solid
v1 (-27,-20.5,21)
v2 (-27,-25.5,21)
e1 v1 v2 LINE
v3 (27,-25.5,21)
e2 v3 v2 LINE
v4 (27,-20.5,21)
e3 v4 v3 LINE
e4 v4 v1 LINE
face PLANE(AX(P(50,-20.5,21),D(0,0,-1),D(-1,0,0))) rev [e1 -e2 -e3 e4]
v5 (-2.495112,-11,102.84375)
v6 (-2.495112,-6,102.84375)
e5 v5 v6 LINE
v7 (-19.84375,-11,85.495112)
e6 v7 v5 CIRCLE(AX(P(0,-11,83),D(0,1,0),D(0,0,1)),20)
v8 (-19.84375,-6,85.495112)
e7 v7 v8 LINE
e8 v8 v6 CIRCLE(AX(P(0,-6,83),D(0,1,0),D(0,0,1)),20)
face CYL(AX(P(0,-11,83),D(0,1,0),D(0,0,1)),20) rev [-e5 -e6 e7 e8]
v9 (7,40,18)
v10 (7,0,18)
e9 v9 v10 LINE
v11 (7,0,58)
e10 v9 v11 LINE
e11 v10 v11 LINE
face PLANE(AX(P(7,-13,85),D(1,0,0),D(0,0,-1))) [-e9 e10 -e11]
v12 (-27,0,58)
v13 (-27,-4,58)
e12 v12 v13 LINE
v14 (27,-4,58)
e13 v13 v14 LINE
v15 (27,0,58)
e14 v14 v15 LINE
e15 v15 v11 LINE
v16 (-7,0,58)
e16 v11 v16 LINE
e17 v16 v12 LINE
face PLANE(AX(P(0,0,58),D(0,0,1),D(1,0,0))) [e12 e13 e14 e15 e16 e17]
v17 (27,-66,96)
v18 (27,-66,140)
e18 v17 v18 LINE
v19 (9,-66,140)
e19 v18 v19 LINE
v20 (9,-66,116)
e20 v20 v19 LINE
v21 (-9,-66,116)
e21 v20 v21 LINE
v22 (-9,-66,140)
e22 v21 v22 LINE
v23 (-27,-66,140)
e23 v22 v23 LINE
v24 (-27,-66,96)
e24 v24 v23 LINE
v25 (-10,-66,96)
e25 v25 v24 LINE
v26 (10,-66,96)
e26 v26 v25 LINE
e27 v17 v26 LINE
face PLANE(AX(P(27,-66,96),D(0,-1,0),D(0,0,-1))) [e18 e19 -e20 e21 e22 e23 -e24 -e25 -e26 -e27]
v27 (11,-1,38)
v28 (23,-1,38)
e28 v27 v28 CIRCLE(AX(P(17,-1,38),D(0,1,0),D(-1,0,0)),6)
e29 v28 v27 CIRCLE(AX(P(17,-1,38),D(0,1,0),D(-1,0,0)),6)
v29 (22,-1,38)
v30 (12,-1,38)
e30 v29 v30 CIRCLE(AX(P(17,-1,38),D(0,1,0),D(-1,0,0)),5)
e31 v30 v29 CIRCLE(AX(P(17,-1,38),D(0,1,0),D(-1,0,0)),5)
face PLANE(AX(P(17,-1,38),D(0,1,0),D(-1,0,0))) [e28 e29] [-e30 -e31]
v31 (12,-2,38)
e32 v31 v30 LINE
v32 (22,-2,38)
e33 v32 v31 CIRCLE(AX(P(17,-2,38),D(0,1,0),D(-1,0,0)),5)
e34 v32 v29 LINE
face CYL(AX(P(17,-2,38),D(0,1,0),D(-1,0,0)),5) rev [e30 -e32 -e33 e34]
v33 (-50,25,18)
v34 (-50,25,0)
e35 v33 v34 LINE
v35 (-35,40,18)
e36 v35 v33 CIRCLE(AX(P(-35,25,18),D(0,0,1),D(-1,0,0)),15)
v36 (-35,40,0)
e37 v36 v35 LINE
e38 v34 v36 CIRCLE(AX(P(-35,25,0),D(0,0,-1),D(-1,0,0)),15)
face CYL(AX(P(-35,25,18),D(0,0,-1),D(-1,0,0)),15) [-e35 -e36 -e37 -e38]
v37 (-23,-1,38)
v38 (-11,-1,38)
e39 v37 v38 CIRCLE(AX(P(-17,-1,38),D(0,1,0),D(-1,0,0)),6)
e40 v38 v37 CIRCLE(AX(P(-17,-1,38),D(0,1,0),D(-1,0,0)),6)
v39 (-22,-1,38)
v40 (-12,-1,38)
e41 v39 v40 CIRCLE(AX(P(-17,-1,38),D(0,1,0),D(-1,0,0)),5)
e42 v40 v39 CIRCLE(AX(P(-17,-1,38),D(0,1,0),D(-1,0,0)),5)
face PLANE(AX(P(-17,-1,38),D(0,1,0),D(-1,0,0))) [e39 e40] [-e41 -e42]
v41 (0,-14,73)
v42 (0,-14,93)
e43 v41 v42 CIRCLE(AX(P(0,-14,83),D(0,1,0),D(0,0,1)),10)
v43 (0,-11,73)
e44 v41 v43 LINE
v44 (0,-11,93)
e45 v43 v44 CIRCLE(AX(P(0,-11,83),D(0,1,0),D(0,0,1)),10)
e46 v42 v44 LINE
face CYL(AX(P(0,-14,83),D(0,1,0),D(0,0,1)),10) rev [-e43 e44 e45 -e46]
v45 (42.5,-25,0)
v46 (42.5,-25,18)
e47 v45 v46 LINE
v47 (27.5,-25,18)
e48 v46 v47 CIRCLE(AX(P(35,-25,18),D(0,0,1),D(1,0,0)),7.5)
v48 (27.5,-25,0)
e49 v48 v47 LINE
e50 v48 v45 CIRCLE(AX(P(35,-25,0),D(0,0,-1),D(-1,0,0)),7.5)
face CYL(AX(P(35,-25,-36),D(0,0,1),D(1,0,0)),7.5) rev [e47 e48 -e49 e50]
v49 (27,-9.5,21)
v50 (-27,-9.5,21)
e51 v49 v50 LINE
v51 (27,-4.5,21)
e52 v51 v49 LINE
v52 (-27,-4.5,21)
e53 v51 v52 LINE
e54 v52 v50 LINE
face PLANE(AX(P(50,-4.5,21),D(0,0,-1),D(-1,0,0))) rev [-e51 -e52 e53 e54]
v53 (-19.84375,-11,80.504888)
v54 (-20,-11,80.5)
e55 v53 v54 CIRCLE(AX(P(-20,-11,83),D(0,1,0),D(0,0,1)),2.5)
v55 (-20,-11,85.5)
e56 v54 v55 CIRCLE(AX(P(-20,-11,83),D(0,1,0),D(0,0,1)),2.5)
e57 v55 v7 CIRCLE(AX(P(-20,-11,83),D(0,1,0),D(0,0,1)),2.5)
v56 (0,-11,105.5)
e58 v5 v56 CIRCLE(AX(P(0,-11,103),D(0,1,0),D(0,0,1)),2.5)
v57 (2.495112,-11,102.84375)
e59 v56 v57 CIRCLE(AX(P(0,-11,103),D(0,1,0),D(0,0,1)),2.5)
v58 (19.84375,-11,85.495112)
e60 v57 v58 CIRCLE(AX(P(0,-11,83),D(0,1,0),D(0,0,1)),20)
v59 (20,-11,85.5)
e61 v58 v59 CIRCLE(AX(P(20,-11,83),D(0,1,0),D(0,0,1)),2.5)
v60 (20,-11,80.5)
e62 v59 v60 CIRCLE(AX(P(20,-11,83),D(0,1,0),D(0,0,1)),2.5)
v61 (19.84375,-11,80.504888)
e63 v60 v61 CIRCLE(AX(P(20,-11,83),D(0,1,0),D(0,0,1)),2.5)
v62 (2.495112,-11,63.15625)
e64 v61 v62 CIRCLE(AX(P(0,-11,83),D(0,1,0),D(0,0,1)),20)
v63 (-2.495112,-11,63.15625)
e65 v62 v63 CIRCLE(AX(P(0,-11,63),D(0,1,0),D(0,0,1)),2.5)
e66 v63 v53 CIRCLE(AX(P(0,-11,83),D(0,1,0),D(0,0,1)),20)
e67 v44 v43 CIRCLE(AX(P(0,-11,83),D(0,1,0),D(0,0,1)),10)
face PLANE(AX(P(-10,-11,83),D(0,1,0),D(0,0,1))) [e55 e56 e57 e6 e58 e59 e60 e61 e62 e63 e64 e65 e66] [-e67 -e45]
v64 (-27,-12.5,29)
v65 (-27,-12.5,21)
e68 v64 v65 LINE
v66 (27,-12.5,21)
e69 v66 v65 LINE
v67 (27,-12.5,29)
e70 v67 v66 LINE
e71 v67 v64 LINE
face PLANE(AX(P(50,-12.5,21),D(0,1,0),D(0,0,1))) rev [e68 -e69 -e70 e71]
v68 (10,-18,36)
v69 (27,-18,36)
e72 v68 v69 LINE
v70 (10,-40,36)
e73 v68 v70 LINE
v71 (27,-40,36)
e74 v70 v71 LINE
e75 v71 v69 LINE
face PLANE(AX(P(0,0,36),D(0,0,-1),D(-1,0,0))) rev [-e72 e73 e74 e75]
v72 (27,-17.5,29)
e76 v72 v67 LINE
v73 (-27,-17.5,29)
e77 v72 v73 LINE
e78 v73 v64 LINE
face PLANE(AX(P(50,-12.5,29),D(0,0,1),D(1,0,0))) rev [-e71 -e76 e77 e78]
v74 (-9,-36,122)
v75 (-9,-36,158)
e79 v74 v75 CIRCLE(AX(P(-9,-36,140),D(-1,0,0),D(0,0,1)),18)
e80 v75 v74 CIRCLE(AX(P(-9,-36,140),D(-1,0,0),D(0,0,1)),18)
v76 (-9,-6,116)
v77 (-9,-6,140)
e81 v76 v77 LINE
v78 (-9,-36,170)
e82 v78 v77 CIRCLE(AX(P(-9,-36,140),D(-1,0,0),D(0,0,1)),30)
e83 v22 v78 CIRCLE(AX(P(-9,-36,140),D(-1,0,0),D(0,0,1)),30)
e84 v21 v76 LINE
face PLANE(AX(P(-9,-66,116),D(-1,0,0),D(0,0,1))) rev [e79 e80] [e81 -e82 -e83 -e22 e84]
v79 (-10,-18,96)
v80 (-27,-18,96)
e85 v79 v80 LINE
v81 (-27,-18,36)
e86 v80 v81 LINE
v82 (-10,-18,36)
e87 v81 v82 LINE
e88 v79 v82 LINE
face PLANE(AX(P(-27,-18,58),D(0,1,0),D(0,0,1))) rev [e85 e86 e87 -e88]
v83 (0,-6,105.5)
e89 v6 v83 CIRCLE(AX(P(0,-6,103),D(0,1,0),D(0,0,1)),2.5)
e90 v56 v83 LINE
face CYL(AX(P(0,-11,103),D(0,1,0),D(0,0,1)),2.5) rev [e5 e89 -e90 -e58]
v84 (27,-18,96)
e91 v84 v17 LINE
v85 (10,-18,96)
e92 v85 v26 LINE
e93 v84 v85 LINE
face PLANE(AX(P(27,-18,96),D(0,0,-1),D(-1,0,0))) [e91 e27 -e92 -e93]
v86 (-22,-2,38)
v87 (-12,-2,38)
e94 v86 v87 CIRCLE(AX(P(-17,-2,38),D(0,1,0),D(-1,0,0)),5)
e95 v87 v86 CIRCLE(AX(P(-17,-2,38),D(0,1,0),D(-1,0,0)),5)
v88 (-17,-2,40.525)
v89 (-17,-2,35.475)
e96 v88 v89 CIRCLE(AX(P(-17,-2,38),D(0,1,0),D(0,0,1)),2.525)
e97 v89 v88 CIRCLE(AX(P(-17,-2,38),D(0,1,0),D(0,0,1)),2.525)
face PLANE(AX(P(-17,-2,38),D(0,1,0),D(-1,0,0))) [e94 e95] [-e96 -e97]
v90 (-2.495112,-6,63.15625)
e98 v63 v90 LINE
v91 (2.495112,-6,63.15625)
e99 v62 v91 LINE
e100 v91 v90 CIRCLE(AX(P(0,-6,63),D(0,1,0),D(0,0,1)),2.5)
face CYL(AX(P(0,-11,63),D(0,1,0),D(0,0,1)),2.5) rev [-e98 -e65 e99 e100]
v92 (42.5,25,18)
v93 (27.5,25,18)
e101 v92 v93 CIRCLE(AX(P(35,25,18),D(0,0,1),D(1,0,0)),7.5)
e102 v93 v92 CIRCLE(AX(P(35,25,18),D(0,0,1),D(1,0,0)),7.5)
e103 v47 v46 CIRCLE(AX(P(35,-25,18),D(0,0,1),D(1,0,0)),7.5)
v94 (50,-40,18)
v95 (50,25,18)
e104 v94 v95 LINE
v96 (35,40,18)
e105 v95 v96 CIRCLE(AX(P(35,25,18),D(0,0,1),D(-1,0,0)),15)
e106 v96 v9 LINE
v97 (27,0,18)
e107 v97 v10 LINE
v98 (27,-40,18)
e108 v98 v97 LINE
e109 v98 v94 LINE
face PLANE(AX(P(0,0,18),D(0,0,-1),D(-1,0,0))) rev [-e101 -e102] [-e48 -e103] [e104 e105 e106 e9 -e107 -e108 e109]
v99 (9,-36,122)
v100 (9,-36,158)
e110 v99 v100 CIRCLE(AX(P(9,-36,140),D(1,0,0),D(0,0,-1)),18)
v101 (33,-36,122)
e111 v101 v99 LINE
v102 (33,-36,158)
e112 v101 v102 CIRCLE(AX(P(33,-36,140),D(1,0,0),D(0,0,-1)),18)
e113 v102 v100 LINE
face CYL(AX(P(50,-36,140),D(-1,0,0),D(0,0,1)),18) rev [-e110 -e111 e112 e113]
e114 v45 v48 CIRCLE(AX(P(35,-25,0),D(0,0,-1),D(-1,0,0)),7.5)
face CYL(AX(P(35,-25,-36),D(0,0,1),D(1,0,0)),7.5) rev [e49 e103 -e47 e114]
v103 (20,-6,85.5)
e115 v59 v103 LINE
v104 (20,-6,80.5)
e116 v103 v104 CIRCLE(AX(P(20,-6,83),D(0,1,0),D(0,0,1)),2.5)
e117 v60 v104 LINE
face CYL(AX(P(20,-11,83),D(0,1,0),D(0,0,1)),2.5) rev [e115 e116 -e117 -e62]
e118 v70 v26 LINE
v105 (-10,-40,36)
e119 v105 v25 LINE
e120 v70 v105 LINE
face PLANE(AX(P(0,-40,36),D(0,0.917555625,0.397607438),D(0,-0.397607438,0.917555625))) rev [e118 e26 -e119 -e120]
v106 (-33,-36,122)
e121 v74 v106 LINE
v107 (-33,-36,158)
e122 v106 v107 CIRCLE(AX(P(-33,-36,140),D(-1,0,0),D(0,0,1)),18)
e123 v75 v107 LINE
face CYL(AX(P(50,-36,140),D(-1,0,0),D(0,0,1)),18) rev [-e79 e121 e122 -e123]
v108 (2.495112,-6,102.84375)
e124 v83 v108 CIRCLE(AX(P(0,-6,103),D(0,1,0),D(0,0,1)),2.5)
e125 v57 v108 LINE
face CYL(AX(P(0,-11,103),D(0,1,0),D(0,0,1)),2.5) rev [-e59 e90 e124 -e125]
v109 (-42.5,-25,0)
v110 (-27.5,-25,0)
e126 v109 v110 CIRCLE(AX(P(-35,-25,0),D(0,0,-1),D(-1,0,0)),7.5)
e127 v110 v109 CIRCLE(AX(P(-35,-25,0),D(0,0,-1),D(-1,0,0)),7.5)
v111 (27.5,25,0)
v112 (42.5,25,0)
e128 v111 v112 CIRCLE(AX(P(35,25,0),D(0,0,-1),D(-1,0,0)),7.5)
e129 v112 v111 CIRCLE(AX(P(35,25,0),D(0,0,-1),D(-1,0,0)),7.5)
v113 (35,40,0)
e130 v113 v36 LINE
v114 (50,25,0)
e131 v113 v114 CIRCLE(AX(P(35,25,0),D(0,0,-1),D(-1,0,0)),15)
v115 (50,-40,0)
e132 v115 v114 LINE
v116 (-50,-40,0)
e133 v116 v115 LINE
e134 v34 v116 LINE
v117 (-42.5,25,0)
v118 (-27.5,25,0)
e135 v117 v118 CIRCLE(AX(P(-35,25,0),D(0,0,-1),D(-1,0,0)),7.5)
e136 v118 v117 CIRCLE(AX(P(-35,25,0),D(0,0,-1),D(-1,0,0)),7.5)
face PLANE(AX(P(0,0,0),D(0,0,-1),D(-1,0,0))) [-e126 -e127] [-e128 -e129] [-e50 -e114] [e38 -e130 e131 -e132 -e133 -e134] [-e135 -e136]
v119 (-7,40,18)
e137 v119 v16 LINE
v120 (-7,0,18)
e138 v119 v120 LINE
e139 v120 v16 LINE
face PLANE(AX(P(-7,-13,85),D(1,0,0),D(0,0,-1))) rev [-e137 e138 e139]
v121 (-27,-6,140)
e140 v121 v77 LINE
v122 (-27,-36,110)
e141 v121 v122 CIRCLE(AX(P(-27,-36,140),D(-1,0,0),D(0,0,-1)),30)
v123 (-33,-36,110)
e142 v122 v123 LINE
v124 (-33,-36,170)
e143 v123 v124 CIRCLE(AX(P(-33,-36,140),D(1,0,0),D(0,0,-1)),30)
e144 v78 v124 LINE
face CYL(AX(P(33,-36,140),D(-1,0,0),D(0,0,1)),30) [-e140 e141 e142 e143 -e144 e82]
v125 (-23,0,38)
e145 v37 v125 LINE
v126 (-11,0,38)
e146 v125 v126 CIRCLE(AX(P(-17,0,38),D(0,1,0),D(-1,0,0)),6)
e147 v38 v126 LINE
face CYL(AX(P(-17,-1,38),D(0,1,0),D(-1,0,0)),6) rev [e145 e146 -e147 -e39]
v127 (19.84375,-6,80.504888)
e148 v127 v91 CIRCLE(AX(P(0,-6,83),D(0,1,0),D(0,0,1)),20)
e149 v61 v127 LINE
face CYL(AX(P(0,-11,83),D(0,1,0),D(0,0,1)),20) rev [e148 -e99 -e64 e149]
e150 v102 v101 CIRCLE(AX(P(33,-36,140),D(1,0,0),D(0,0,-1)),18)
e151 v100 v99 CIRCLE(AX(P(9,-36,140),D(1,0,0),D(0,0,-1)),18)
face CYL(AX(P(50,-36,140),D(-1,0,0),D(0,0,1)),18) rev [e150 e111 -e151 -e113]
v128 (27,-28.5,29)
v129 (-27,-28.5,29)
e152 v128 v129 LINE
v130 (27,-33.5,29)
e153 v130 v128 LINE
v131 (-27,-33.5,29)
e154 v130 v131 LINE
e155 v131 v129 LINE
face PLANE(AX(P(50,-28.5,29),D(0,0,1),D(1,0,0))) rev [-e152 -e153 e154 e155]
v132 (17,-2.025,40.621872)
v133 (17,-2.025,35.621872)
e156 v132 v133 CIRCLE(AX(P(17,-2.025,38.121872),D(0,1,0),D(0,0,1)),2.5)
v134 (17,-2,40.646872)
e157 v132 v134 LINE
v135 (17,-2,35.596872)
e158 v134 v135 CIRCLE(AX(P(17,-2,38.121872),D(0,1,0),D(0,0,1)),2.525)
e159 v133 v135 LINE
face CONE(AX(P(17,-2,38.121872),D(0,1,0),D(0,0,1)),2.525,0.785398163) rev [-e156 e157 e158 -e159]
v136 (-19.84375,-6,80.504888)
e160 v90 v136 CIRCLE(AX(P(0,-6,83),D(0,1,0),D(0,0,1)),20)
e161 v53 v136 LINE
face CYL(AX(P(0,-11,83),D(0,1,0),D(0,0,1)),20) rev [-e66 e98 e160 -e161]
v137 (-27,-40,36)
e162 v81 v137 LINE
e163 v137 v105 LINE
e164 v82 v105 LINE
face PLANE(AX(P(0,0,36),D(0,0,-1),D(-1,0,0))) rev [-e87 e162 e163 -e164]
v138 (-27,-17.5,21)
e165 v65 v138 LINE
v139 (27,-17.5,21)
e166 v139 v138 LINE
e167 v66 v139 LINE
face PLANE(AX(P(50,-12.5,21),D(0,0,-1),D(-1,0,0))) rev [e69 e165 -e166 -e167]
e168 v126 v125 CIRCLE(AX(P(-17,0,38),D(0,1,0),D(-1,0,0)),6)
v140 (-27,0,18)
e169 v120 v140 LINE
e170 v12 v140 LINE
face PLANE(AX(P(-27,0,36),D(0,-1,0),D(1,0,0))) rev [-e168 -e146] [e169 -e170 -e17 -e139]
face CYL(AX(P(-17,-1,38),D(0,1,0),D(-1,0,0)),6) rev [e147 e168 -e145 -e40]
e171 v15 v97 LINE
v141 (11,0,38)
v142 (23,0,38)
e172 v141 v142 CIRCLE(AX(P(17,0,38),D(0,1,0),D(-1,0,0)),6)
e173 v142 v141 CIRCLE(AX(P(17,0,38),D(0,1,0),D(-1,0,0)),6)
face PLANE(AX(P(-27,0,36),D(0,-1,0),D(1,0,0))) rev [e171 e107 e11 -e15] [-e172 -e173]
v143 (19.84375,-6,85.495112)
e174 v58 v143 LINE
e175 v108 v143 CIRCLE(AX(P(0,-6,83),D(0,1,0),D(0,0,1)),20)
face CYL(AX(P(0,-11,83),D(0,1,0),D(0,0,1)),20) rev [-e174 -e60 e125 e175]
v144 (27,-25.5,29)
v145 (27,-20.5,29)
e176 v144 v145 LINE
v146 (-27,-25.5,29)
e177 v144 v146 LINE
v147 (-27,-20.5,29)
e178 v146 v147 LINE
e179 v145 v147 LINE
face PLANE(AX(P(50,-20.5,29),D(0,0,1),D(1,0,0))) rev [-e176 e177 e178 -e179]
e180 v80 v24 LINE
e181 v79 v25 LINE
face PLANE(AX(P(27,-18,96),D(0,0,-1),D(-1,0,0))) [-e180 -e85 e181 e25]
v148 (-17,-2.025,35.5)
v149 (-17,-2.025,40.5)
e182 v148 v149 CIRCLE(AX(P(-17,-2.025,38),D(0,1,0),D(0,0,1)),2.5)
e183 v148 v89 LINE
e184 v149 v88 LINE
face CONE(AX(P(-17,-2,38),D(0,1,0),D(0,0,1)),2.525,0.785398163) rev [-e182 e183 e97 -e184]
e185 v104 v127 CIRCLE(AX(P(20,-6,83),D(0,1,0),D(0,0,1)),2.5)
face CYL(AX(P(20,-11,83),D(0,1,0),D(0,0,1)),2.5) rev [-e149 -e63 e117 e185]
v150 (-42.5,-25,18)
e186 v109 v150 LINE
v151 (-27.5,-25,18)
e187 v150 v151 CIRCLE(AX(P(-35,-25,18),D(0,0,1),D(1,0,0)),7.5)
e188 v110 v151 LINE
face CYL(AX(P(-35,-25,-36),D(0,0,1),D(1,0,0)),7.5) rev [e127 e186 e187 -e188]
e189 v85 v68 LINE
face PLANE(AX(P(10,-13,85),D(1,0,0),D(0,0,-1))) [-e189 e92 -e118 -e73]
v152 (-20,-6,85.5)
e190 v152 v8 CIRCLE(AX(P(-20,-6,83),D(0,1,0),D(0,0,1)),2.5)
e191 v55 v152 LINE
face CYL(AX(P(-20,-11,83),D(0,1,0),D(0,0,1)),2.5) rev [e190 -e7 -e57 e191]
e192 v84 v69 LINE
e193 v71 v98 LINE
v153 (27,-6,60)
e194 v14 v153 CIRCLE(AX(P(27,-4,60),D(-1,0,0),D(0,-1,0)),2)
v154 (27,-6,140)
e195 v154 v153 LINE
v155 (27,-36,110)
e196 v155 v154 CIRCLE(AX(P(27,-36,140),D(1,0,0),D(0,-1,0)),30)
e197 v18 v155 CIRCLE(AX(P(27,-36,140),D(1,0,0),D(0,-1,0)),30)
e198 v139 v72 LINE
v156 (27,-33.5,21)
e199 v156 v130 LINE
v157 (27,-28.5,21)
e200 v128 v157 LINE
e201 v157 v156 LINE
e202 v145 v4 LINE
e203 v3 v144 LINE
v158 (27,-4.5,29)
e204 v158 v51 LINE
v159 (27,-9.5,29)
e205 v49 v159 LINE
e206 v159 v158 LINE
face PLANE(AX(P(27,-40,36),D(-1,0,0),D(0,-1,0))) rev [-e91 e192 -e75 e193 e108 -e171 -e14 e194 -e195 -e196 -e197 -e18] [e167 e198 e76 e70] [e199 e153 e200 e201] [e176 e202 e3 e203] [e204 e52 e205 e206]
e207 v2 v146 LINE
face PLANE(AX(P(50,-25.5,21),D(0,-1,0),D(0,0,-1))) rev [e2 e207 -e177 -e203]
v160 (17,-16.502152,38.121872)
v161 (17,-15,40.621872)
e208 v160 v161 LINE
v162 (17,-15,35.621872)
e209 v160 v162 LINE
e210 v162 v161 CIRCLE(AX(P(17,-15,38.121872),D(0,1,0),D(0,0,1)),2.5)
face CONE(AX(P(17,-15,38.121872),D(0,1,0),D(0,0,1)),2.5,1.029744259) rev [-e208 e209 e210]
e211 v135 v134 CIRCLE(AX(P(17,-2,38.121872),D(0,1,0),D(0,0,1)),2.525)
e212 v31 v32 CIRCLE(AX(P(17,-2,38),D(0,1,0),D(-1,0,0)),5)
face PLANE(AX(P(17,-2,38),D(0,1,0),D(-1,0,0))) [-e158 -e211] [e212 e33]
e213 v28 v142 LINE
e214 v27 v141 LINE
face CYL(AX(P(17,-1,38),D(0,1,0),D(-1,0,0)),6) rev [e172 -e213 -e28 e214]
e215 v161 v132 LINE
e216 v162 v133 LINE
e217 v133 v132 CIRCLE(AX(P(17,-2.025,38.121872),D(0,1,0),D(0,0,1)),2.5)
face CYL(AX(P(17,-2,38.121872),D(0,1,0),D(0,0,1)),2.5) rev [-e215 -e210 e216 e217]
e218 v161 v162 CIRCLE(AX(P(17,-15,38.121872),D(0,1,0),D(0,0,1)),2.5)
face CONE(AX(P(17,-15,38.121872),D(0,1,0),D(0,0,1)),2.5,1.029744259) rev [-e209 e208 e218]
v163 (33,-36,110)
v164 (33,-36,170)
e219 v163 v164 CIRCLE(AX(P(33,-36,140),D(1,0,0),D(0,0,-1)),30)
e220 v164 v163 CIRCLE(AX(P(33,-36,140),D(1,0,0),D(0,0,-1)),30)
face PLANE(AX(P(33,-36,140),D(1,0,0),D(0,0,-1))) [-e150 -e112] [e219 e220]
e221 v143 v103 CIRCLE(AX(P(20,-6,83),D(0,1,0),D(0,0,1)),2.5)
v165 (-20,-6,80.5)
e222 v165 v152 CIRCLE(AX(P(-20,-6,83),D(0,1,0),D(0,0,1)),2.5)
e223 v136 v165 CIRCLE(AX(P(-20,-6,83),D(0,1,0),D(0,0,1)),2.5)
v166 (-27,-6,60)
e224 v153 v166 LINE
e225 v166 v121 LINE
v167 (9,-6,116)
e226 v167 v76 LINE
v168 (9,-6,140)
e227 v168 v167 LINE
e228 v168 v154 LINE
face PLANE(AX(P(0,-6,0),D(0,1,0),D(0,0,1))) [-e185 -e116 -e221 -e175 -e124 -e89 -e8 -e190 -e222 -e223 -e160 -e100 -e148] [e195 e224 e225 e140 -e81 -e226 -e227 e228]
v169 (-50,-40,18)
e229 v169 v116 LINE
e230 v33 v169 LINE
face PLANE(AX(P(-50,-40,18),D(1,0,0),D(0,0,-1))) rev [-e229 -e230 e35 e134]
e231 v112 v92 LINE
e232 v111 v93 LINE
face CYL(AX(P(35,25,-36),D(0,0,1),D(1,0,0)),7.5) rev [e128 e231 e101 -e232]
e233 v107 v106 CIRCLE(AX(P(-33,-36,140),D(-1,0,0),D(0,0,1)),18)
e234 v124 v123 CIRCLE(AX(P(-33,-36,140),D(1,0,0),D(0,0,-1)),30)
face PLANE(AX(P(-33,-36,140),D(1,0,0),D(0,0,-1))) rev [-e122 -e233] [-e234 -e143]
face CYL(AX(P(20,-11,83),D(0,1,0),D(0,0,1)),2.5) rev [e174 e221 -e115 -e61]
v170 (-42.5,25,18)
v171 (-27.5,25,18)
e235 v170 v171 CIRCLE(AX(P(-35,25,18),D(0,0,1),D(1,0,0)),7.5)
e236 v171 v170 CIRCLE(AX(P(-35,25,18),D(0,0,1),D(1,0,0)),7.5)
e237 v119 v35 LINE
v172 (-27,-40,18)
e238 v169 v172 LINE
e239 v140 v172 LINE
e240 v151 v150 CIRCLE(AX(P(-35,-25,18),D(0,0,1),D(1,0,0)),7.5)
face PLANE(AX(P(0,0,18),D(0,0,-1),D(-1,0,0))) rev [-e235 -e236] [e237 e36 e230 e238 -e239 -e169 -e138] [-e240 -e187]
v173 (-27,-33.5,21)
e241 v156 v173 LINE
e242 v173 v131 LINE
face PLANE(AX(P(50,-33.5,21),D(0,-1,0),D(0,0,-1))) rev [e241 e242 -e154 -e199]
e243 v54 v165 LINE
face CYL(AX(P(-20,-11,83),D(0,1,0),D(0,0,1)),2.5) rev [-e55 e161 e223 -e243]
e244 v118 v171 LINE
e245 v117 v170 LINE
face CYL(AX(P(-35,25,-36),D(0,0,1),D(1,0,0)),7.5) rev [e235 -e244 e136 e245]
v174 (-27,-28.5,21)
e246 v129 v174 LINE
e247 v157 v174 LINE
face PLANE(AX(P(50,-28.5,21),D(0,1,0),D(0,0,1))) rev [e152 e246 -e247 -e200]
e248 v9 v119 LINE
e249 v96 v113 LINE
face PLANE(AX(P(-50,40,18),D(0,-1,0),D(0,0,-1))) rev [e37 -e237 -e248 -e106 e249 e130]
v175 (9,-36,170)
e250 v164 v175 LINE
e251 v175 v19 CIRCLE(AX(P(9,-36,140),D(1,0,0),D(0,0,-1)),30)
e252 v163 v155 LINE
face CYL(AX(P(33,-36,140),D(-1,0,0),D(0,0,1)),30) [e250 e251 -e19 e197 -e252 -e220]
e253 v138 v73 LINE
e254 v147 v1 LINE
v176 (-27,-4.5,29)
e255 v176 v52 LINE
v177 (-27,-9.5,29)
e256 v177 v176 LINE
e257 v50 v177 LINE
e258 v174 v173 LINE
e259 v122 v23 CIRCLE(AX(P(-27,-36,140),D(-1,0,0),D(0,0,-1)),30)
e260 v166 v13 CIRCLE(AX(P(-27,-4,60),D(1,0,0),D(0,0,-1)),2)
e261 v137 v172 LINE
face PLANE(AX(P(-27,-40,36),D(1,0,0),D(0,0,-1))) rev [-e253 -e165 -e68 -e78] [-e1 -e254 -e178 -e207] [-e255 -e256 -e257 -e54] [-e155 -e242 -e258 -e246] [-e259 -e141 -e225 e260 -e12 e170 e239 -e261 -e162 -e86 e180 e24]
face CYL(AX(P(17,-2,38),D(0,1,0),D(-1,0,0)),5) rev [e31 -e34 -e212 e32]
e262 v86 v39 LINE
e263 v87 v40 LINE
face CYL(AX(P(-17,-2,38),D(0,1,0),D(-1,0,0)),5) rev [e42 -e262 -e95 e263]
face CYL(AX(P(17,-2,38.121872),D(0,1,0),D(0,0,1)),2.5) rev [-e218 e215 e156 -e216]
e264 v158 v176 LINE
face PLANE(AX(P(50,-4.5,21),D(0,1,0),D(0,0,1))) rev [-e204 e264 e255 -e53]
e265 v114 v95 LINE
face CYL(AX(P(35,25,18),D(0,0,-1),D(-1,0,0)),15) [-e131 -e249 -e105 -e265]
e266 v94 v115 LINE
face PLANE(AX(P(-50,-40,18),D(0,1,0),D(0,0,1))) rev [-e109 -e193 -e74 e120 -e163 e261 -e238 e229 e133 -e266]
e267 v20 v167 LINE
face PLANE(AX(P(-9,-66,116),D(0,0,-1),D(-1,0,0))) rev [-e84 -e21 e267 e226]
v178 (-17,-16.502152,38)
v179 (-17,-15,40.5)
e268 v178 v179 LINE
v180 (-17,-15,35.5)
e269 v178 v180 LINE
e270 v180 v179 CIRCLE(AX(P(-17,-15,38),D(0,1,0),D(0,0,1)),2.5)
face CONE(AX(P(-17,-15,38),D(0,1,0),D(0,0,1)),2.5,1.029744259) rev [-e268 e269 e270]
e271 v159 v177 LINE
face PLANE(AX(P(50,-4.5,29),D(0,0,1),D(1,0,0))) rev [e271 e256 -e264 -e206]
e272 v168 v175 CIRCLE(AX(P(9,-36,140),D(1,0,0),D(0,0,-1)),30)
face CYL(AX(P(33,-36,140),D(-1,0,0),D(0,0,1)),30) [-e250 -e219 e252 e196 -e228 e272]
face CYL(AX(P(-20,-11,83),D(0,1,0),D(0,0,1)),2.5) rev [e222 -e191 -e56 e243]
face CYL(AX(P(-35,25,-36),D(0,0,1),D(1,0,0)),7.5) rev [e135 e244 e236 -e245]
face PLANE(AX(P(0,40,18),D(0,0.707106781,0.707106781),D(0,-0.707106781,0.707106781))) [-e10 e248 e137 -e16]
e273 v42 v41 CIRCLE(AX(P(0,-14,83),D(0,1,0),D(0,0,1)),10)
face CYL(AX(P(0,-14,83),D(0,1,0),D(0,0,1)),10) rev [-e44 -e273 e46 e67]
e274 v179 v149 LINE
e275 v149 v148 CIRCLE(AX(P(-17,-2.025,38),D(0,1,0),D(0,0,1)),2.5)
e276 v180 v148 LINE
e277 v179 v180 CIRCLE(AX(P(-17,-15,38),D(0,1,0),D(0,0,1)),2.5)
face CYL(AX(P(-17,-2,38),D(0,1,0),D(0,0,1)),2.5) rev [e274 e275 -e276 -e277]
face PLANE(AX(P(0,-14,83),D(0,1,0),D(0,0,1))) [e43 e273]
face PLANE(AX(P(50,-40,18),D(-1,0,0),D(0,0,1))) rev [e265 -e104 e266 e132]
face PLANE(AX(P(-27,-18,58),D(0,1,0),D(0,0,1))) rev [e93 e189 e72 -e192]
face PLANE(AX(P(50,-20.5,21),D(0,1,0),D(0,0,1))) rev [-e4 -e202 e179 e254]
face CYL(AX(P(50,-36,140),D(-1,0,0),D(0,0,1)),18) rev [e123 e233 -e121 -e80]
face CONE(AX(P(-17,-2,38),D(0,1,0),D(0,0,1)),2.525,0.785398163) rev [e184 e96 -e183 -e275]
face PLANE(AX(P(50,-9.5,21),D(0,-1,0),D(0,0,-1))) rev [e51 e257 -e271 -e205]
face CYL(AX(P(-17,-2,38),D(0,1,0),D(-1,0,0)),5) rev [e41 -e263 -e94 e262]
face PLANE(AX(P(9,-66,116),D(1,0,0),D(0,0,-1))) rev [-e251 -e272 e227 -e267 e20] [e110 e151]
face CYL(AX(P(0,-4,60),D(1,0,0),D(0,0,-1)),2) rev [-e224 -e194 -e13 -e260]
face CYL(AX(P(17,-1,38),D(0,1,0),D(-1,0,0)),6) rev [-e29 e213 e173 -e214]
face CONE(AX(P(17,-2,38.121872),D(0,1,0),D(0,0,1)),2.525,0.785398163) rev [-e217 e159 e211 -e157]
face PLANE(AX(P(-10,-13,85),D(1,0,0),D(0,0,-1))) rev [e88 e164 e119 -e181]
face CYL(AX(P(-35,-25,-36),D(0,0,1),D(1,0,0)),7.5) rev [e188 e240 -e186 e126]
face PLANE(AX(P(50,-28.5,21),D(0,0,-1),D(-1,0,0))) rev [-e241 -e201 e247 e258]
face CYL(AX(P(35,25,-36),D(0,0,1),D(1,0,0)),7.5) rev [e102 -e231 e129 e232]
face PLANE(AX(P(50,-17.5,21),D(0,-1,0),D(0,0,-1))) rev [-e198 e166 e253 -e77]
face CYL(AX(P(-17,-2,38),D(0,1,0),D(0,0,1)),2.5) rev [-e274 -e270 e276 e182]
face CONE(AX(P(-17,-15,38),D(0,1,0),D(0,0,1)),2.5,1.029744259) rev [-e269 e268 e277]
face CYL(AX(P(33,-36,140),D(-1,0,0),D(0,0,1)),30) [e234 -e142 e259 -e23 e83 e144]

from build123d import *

# Parameters (mm, degrees)
MOUNTING_PLATE_SKETCH_W       = 100
MOUNTING_PLATE_SKETCH_H       = 80
MOUNTING_PLATE_DEPTH          = 18
SUPPORT_BLOCK_SKETCH_W        = 54
SUPPORT_BLOCK_SKETCH_H        = 40
SUPPORT_BLOCK_DEPTH           = 18
ARM_EXTENSION_SKETCH_W        = 54
ARM_EXTENSION_SKETCH_H        = 18
ARM_EXTENSION_DEPTH           = 22
CLEVIS_EYE_SKETCH_R           = 30
CLEVIS_EYE_BOSS_DEPTH         = 33
ARM_TOP_PLATE_SKETCH_W        = 54
ARM_TOP_PLATE_SKETCH_H        = 82
ARM_TOP_PLATE_DEPTH           = 12
CLEVIS_NECK_SKETCH_W          = 44
CLEVIS_NECK_SKETCH_H          = 48
CLEVIS_NECK_DEPTH             = 54
LOWER_RIB_20_REACH            = 191.093
LOWER_RIB_SKETCH_WALL_W       = 445.576270742
LOWER_RIB_SKETCH_WALL_H       = 20
PLATE_GUSSET_14_REACH         = 191.093
PLATE_GUSSET_SKETCH_WALL_W    = 436.75368234
PLATE_GUSSET_SKETCH_WALL_H    = 14
PLATE_CORNER_FILLETS_R15_R    = 15
RELIEF_NOTCH_SKETCH_R         = 7.5
RELIEF_NOTCH_15X15_DEPTH      = 54
LOCATING_STEP_SKETCH_R        = 6
LOCATING_STEP_1MM_DEPTH       = 1
LOCATING_GROOVE_SKETCH_R      = 5
LOCATING_GROOVE_1MM_DEPTH     = 1
DOWEL_HOLE_5_D                = 5
DOWEL_HOLE_5_DEPTH            = 13
DOWEL_HOLE_5_CSINK_D          = 5.05
DOWEL_HOLE_5_CSINK_ANGLE      = 90
DOWEL_HOLE_5_TIP              = 1.502151548
SIDE_SLOTS_SKETCH_W           = 8
SIDE_SLOTS_SKETCH_H           = 5
SIDE_SLOTS_4X_DEPTH           = 198.952014387
BEARING_RECESS_65_KEYED_DEPTH = 5
CENTRE_RECESS_SKETCH_R        = 10
CENTRE_RECESS_20_DEPTH        = 3
CLEVIS_SLOT_SKETCH_W          = 18
CLEVIS_SLOT_SKETCH_H          = 73.376983309
CLEVIS_SLOT_24_DEPTH          = 188.082869339
CLEVIS_BORE_SKETCH_R          = 18
CLEVIS_BORE_36_DEPTH          = 201.362172078
EDGE_FILLETS_R2_R             = 2


with BuildPart() as part:
    # Mounting Plate Sketch → Mounting Plate (new body)
    with BuildSketch(Plane.XY):
        Rectangle(MOUNTING_PLATE_SKETCH_W, MOUNTING_PLATE_SKETCH_H)
    extrude(amount=MOUNTING_PLATE_DEPTH)

    # Support Block Sketch → Support Block (add)
    with BuildSketch(Plane.XY.offset(18)):
        with Locations((0, -20)):
            Rectangle(SUPPORT_BLOCK_SKETCH_W, SUPPORT_BLOCK_SKETCH_H)
    extrude(amount=SUPPORT_BLOCK_DEPTH)

    # Arm Extension Sketch → Arm Extension (add)
    with BuildSketch(Plane.XY.offset(36)):
        with Locations((0, -9)):
            Rectangle(ARM_EXTENSION_SKETCH_W, ARM_EXTENSION_SKETCH_H)
    extrude(amount=ARM_EXTENSION_DEPTH)



with BuildPart() as body_2:
    # Clevis Eye Sketch → Clevis Eye Boss (new, symmetric)
    with BuildSketch(Plane(origin=(0, 0, 0), x_dir=(0, 0, -1), z_dir=(1, 0, 0))):
        with Locations((-140, -36)):
            Circle(CLEVIS_EYE_SKETCH_R)
    extrude(amount=CLEVIS_EYE_BOSS_DEPTH, both=True)


with BuildPart() as part_1:
    add(part.part)

    add(body_2.part)  # Arm Top Plate merges body 2
    # Arm Top Plate Sketch → Arm Top Plate (add)
    with BuildSketch(Plane(origin=(0, -6, 0), x_dir=(1, 0, 0), z_dir=(0, 1, 0))):
        with Locations((0, -99)):
            Rectangle(ARM_TOP_PLATE_SKETCH_W, ARM_TOP_PLATE_SKETCH_H)
    extrude(amount=-ARM_TOP_PLATE_DEPTH)

    # Clevis Neck Sketch → Clevis Neck (add)
    with BuildSketch(Plane.ZY.offset(27)):
        with Locations((118, -42)):
            Rectangle(CLEVIS_NECK_SKETCH_W, CLEVIS_NECK_SKETCH_H)
    extrude(amount=-CLEVIS_NECK_DEPTH)

    # Lower Rib Sketch wall → Lower Rib 20 (add, up to next)
    with BuildSketch(Plane(origin=(0, -53, 66), x_dir=(0, -0.397607437634, 0.91755562531), z_dir=(0, -0.91755562531, -0.397607437634)), mode=Mode.PRIVATE) as lower_rib_20_sk1:
        Rectangle(LOWER_RIB_SKETCH_WALL_W, LOWER_RIB_SKETCH_WALL_H)
    lower_rib_20_tool1 = extrude(lower_rib_20_sk1.sketch, amount=-LOWER_RIB_20_REACH, mode=Mode.PRIVATE) - part_1.part
    add(lower_rib_20_tool1.solids().sort_by_distance((0, -53, 66))[0])

    # Plate Gusset Sketch wall → Plate Gusset 14 (add, up to next)
    with BuildSketch(Plane(origin=(0, 20, 38), x_dir=(0, -0.707106781187, 0.707106781187), z_dir=(0, -0.707106781187, -0.707106781187)), mode=Mode.PRIVATE) as plate_gusset_14_sk1:
        Rectangle(PLATE_GUSSET_SKETCH_WALL_W, PLATE_GUSSET_SKETCH_WALL_H)
    plate_gusset_14_tool1 = extrude(plate_gusset_14_sk1.sketch, amount=PLATE_GUSSET_14_REACH, mode=Mode.PRIVATE) - part_1.part
    add(plate_gusset_14_tool1.solids().sort_by_distance((0, 20, 38))[0])

    # Plate Corner Fillets R15
    plate_corner_fillets_r15_edges = [part_1.edges().sort_by_distance(p)[0] for p in [
        (-50, 40, 9),
        (50, 40, 9),
    ]]
    fillet(plate_corner_fillets_r15_edges, radius=PLATE_CORNER_FILLETS_R15_R)

    # Relief Notch Sketch → Relief Notch 15x15 (cut)
    with BuildSketch(Plane.XY.offset(18)):
        with Locations((-35, 25)):
            Circle(RELIEF_NOTCH_SKETCH_R)
        with Locations((-35, -25)):
            Circle(RELIEF_NOTCH_SKETCH_R)
        with Locations((35, 25)):
            Circle(RELIEF_NOTCH_SKETCH_R)
        with Locations((35, -25)):
            Circle(RELIEF_NOTCH_SKETCH_R)
    extrude(amount=-RELIEF_NOTCH_15X15_DEPTH, mode=Mode.SUBTRACT)

    # Locating Step Sketch → Locating Step 1mm (cut)
    with BuildSketch(Plane(origin=(0, 0, 0), x_dir=(1, 0, 0), z_dir=(0, 1, 0))):
        with Locations(Location((-17, -38, 0), (0, 0, 180))):
            Circle(LOCATING_STEP_SKETCH_R)
        with Locations(Location((17, -38, 0), (0, 0, 180))):
            Circle(LOCATING_STEP_SKETCH_R)
    extrude(amount=-LOCATING_STEP_1MM_DEPTH, mode=Mode.SUBTRACT)

    # Locating Groove Sketch → Locating Groove 1mm (cut)
    with BuildSketch(Plane(origin=(0, -1, 0), x_dir=(1, 0, 0), z_dir=(0, 1, 0))):
        with Locations(Location((-17, -38, 0), (0, 0, 180))):
            Circle(LOCATING_GROOVE_SKETCH_R)
        with Locations(Location((17, -38, 0), (0, 0, 180))):
            Circle(LOCATING_GROOVE_SKETCH_R)
    extrude(amount=-LOCATING_GROOVE_1MM_DEPTH, mode=Mode.SUBTRACT)

    # Dowel Hole Ø5
    with Locations(Plane(origin=(0, -2, 0), x_dir=(1, 0, 0), z_dir=(0, 1, 0))):
        with Locations((-17, -38), (17, -38.121872411)):
            CounterSinkHole(DOWEL_HOLE_5_D / 2, DOWEL_HOLE_5_CSINK_D / 2, depth=DOWEL_HOLE_5_DEPTH, counter_sink_angle=DOWEL_HOLE_5_CSINK_ANGLE)
            with Locations((0, 0, -(DOWEL_HOLE_5_DEPTH + DOWEL_HOLE_5_TIP / 2))):  # 118° drill point
                Cone(0, DOWEL_HOLE_5_D / 2, DOWEL_HOLE_5_TIP, mode=Mode.SUBTRACT)

    # Side Slots Sketch → Side Slots 4x (cut, through all)
    with BuildSketch(Plane.ZY.offset(27)):
        with Locations((25, -7)):
            Rectangle(SIDE_SLOTS_SKETCH_W, SIDE_SLOTS_SKETCH_H)
        with Locations((25, -15)):
            Rectangle(SIDE_SLOTS_SKETCH_W, SIDE_SLOTS_SKETCH_H)
        with Locations((25, -23)):
            Rectangle(SIDE_SLOTS_SKETCH_W, SIDE_SLOTS_SKETCH_H)
        with Locations((25, -31)):
            Rectangle(SIDE_SLOTS_SKETCH_W, SIDE_SLOTS_SKETCH_H)
    extrude(amount=-SIDE_SLOTS_4X_DEPTH, mode=Mode.SUBTRACT)

    # Bearing Recess Sketch → Bearing Recess Ø65 Keyed (cut)
    with BuildSketch(Plane(origin=(0, -6, 0), x_dir=(1, 0, 0), z_dir=(0, 1, 0))):
        with BuildLine():
            ThreePointArc((-19.84375, -85.49511241), (-14.142135624, -97.142135624), (-2.49511241, -102.84375))
            ThreePointArc((-2.49511241, -102.84375), (0, -105.5), (2.49511241, -102.84375))
            ThreePointArc((2.49511241, -102.84375), (14.142135624, -97.142135624), (19.84375, -85.49511241))
            ThreePointArc((19.84375, -85.49511241), (22.5, -83), (19.84375, -80.50488759))
            ThreePointArc((19.84375, -80.50488759), (14.142135624, -68.857864376), (2.49511241, -63.15625))
            ThreePointArc((2.49511241, -63.15625), (0, -60.5), (-2.49511241, -63.15625))
            ThreePointArc((-2.49511241, -63.15625), (-14.142135624, -68.857864376), (-19.84375, -80.50488759))
            ThreePointArc((-19.84375, -80.50488759), (-22.5, -83), (-19.84375, -85.49511241))
        make_face()
    extrude(amount=-BEARING_RECESS_65_KEYED_DEPTH, mode=Mode.SUBTRACT)

    # Centre Recess Sketch → Centre Recess Ø20 (cut)
    with BuildSketch(Plane(origin=(0, -11, 0), x_dir=(1, 0, 0), z_dir=(0, 1, 0))):
        with Locations(Location((0, -83, 0), (0, 0, 270))):
            Circle(CENTRE_RECESS_SKETCH_R)
    extrude(amount=-CENTRE_RECESS_20_DEPTH, mode=Mode.SUBTRACT)

    # Clevis Slot Sketch → Clevis Slot 24 (cut, through all)
    with BuildSketch(Plane(origin=(0, -6, 0), x_dir=(1, 0, 0), z_dir=(0, 1, 0))):
        with Locations((0, -152.688491655)):
            Rectangle(CLEVIS_SLOT_SKETCH_W, CLEVIS_SLOT_SKETCH_H)
    extrude(amount=-CLEVIS_SLOT_24_DEPTH, mode=Mode.SUBTRACT)

    # Clevis Bore Sketch → Clevis Bore Ø36 (cut, through all)
    with BuildSketch(Plane.ZY.offset(33)):
        with Locations(Location((140, -36, 0), (0, 0, 180))):
            Circle(CLEVIS_BORE_SKETCH_R)
    extrude(amount=-CLEVIS_BORE_36_DEPTH, mode=Mode.SUBTRACT)

    # Edge Fillets R2
    edge_fillets_r2_edges = [part_1.edges().sort_by_distance(p)[0] for p in [
        (0, -6, 58),
    ]]
    fillet(edge_fillets_r2_edges, radius=EDGE_FILLETS_R2_R)


solid = part_1.part
